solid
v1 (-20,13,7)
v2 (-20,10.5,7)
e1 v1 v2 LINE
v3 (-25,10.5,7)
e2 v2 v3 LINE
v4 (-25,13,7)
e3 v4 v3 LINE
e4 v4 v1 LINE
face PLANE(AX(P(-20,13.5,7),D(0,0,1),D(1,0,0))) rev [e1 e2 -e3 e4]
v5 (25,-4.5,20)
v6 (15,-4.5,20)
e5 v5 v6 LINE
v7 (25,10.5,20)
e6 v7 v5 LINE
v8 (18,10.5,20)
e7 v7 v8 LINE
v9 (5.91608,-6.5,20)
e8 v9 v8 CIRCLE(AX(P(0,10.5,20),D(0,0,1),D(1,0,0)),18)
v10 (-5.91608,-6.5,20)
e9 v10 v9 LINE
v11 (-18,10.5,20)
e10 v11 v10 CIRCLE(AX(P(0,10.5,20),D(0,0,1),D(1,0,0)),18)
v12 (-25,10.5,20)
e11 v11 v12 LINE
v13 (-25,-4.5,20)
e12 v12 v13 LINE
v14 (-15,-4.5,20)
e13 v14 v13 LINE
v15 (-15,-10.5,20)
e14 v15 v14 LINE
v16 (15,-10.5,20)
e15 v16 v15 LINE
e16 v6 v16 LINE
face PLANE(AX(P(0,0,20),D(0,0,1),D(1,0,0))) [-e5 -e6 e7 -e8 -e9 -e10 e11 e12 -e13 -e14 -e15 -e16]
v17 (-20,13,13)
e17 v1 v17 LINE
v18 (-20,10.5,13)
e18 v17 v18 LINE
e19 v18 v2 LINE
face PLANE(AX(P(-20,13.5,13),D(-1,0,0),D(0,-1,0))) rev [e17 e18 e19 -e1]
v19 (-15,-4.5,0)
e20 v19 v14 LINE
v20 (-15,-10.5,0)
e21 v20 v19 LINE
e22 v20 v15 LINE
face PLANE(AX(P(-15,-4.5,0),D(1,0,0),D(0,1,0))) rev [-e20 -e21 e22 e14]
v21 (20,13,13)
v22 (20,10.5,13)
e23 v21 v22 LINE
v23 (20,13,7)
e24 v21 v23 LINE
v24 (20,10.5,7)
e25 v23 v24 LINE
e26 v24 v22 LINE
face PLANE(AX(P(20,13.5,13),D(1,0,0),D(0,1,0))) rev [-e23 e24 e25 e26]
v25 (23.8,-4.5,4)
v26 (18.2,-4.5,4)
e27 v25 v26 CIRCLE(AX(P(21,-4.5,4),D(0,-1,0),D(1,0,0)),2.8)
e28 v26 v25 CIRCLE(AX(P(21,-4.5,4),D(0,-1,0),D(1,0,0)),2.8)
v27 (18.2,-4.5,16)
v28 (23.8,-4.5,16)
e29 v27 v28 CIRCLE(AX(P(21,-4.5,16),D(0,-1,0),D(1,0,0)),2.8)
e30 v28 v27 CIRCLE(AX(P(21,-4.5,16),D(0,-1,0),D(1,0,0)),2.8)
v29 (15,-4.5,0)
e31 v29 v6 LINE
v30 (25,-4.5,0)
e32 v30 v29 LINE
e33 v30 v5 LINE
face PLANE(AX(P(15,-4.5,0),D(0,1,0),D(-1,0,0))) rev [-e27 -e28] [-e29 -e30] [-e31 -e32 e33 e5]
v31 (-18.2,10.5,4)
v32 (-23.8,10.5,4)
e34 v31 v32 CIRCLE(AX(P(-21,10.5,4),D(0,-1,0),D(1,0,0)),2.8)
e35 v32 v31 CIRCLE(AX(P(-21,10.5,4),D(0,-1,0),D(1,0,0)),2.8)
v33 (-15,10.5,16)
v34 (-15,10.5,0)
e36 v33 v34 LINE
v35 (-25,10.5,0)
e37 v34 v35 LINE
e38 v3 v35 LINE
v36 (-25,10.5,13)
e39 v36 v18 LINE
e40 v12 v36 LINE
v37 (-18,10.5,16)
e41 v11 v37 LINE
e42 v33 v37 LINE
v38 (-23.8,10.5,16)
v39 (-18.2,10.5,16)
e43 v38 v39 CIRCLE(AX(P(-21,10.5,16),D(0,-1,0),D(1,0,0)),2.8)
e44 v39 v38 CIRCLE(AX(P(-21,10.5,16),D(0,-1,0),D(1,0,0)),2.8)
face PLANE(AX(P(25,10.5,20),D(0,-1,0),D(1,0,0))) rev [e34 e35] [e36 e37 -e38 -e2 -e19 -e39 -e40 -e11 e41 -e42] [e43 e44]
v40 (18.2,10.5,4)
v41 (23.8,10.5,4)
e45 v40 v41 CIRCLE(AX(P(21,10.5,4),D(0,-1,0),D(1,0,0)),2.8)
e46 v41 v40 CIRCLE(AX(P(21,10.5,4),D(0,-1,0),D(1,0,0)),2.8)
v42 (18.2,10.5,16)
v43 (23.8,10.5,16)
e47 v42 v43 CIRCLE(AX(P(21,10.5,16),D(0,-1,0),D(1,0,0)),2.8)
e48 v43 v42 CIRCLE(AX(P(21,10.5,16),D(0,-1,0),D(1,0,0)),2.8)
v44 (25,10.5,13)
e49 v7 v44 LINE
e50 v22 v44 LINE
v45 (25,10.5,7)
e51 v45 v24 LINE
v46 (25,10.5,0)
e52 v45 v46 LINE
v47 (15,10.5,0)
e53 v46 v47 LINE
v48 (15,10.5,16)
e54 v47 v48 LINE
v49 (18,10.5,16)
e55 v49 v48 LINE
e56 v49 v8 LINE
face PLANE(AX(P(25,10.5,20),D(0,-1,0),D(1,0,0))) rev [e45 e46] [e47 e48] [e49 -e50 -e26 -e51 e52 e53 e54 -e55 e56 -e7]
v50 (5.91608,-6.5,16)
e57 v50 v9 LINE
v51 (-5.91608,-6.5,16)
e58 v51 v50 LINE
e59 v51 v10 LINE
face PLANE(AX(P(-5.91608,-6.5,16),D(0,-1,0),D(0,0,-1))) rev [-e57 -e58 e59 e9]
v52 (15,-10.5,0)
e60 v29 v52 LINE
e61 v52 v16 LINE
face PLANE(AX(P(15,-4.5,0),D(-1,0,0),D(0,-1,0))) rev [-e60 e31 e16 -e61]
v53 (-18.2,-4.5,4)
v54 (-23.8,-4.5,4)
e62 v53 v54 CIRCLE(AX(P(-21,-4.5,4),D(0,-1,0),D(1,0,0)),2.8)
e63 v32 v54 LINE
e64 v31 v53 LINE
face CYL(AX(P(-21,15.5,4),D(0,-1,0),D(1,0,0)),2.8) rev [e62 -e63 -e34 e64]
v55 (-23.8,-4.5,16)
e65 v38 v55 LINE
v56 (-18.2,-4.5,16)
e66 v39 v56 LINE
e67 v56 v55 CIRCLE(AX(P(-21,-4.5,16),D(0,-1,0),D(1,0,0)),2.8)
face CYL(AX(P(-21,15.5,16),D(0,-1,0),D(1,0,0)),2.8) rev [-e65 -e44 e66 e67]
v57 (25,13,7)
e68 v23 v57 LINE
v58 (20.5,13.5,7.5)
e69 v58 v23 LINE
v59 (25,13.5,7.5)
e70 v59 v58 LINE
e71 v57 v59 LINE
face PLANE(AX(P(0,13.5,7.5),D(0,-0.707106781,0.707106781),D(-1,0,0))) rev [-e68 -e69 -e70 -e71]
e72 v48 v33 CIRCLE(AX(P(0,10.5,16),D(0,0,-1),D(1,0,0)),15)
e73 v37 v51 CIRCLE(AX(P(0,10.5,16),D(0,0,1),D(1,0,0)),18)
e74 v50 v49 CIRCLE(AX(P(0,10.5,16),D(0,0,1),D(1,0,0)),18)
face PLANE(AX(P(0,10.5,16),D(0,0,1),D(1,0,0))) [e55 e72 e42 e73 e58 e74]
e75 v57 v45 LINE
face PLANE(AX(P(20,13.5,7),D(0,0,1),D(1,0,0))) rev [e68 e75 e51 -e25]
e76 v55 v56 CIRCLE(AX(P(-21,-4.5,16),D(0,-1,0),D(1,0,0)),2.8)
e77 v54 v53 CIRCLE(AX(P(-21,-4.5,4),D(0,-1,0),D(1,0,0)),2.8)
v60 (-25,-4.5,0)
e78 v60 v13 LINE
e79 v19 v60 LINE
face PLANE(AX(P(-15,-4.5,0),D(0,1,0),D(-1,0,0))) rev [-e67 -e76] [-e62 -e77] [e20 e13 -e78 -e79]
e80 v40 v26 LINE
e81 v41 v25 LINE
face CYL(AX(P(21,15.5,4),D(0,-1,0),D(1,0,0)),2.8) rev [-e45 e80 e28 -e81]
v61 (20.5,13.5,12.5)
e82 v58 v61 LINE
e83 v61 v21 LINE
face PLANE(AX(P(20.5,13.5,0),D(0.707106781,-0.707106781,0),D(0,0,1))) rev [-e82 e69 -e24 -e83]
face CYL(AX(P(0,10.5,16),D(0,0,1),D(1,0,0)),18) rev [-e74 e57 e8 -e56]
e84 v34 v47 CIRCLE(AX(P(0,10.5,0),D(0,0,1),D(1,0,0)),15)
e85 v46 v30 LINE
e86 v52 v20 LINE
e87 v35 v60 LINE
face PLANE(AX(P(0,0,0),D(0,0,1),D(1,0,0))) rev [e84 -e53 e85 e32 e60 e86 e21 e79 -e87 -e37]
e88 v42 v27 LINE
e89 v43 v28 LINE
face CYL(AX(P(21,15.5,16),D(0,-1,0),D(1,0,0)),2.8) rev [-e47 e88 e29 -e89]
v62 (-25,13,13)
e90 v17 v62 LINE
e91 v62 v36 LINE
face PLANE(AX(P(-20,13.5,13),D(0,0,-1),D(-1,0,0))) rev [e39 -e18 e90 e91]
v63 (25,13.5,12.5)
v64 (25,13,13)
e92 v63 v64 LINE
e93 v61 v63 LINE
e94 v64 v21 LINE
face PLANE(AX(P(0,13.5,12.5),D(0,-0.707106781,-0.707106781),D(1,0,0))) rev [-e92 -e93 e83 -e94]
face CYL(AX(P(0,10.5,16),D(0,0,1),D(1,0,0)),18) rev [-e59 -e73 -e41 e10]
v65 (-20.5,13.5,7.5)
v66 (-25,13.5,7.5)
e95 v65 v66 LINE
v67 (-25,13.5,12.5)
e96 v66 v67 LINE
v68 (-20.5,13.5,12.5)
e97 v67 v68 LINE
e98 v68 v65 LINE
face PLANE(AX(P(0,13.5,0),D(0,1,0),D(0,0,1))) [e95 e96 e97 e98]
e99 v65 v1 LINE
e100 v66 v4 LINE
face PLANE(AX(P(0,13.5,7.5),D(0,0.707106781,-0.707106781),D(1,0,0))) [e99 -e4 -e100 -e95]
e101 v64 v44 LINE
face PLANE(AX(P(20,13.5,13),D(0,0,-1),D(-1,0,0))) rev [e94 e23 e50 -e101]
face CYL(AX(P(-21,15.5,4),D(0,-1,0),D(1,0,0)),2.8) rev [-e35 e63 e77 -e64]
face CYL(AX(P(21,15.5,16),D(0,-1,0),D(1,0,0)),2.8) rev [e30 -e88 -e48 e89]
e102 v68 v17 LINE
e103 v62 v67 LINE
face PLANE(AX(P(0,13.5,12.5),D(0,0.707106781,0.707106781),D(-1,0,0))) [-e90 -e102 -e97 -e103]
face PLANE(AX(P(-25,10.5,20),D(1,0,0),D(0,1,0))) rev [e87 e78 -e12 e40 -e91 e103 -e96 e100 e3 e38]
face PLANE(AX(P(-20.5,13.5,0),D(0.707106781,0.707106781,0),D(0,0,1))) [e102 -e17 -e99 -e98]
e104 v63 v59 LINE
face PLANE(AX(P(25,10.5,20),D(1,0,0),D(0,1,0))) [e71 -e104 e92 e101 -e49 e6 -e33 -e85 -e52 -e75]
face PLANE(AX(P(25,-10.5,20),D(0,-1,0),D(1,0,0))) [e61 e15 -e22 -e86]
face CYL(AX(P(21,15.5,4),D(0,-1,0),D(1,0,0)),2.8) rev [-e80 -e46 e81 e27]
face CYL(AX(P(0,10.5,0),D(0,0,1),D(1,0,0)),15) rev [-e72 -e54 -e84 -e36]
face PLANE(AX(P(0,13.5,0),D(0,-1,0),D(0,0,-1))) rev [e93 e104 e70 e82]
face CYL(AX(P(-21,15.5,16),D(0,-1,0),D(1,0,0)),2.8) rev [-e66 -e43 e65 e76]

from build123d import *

# Parameters (mm, degrees)
SKETCH1_W           = 50
SKETCH1_H           = 21
BOSS_EXTRUDE1_DEPTH = 20
SKETCH2_R           = 15
CUT_EXTRUDE1_DEPTH  = 20
SKETCH3_W           = 10
SKETCH3_H           = 6
CUT_EXTRUDE2_DEPTH  = 20
SKETCH4_R           = 2.8
CUT_EXTRUDE3_DEPTH  = 20
SKETCH5_W           = 5
SKETCH5_H           = 6
BOSS_EXTRUDE2_DEPTH = 3
CHAMFER2_SIZE       = 0.5
CUT_EXTRUDE4_DEPTH  = 4


with BuildPart() as part:
    # Sketch1 → Boss-Extrude1 (new body)
    with BuildSketch(Plane.XY):
        Rectangle(SKETCH1_W, SKETCH1_H)
    extrude(amount=BOSS_EXTRUDE1_DEPTH)

    # Sketch2 → Cut-Extrude1 (cut)
    with BuildSketch(Plane.XY.offset(20)):
        with Locations((0, 10.5)):
            Circle(SKETCH2_R)
    extrude(amount=-CUT_EXTRUDE1_DEPTH, mode=Mode.SUBTRACT)

    # Sketch3 → Cut-Extrude2 (cut)
    with BuildSketch(Plane.XY.offset(20)):
        with Locations((-20, -7.5)):
            Rectangle(SKETCH3_W, SKETCH3_H)
        with Locations((20, -7.5)):
            Rectangle(SKETCH3_W, SKETCH3_H)
    extrude(amount=-CUT_EXTRUDE2_DEPTH, mode=Mode.SUBTRACT)

    # Sketch4 → Cut-Extrude3 (cut)
    with BuildSketch(Plane.XZ.offset(4.5)):
        with Locations((-21, 16)):
            Circle(SKETCH4_R)
        with Locations((-21, 4)):
            Circle(SKETCH4_R)
        with Locations((21, 16)):
            Circle(SKETCH4_R)
        with Locations((21, 4)):
            Circle(SKETCH4_R)
    extrude(amount=-CUT_EXTRUDE3_DEPTH, mode=Mode.SUBTRACT)

    # Sketch5 → Boss-Extrude2 (add)
    with BuildSketch(Plane(origin=(0, 10.5, 0), x_dir=(1, 0, 0), z_dir=(0, 1, 0))):
        with Locations((-22.5, -10)):
            Rectangle(SKETCH5_W, SKETCH5_H)
        with Locations((22.5, -10)):
            Rectangle(SKETCH5_W, SKETCH5_H)
    extrude(amount=BOSS_EXTRUDE2_DEPTH)

    # Chamfer2
    chamfer2_edges = [part.edges().sort_by_distance(p)[0] for p in [
        (-22.5, 13.5, 13),
        (-20, 13.5, 10),
        (-22.5, 13.5, 7),
        (20, 13.5, 10),
        (22.5, 13.5, 13),
        (22.5, 13.5, 7),
    ]]
    chamfer(chamfer2_edges, length=CHAMFER2_SIZE)

    # Sketch6 → Cut-Extrude4 (cut)
    with BuildSketch(Plane.XY.offset(20)):
        with BuildLine():
            Line((-5.916079783, -6.5), (5.916079783, -6.5))
            ThreePointArc((5.916079783, -6.5), (0, 28.5), (-5.916079783, -6.5))
        make_face()
    extrude(amount=-CUT_EXTRUDE4_DEPTH, mode=Mode.SUBTRACT)


solid = part.part
